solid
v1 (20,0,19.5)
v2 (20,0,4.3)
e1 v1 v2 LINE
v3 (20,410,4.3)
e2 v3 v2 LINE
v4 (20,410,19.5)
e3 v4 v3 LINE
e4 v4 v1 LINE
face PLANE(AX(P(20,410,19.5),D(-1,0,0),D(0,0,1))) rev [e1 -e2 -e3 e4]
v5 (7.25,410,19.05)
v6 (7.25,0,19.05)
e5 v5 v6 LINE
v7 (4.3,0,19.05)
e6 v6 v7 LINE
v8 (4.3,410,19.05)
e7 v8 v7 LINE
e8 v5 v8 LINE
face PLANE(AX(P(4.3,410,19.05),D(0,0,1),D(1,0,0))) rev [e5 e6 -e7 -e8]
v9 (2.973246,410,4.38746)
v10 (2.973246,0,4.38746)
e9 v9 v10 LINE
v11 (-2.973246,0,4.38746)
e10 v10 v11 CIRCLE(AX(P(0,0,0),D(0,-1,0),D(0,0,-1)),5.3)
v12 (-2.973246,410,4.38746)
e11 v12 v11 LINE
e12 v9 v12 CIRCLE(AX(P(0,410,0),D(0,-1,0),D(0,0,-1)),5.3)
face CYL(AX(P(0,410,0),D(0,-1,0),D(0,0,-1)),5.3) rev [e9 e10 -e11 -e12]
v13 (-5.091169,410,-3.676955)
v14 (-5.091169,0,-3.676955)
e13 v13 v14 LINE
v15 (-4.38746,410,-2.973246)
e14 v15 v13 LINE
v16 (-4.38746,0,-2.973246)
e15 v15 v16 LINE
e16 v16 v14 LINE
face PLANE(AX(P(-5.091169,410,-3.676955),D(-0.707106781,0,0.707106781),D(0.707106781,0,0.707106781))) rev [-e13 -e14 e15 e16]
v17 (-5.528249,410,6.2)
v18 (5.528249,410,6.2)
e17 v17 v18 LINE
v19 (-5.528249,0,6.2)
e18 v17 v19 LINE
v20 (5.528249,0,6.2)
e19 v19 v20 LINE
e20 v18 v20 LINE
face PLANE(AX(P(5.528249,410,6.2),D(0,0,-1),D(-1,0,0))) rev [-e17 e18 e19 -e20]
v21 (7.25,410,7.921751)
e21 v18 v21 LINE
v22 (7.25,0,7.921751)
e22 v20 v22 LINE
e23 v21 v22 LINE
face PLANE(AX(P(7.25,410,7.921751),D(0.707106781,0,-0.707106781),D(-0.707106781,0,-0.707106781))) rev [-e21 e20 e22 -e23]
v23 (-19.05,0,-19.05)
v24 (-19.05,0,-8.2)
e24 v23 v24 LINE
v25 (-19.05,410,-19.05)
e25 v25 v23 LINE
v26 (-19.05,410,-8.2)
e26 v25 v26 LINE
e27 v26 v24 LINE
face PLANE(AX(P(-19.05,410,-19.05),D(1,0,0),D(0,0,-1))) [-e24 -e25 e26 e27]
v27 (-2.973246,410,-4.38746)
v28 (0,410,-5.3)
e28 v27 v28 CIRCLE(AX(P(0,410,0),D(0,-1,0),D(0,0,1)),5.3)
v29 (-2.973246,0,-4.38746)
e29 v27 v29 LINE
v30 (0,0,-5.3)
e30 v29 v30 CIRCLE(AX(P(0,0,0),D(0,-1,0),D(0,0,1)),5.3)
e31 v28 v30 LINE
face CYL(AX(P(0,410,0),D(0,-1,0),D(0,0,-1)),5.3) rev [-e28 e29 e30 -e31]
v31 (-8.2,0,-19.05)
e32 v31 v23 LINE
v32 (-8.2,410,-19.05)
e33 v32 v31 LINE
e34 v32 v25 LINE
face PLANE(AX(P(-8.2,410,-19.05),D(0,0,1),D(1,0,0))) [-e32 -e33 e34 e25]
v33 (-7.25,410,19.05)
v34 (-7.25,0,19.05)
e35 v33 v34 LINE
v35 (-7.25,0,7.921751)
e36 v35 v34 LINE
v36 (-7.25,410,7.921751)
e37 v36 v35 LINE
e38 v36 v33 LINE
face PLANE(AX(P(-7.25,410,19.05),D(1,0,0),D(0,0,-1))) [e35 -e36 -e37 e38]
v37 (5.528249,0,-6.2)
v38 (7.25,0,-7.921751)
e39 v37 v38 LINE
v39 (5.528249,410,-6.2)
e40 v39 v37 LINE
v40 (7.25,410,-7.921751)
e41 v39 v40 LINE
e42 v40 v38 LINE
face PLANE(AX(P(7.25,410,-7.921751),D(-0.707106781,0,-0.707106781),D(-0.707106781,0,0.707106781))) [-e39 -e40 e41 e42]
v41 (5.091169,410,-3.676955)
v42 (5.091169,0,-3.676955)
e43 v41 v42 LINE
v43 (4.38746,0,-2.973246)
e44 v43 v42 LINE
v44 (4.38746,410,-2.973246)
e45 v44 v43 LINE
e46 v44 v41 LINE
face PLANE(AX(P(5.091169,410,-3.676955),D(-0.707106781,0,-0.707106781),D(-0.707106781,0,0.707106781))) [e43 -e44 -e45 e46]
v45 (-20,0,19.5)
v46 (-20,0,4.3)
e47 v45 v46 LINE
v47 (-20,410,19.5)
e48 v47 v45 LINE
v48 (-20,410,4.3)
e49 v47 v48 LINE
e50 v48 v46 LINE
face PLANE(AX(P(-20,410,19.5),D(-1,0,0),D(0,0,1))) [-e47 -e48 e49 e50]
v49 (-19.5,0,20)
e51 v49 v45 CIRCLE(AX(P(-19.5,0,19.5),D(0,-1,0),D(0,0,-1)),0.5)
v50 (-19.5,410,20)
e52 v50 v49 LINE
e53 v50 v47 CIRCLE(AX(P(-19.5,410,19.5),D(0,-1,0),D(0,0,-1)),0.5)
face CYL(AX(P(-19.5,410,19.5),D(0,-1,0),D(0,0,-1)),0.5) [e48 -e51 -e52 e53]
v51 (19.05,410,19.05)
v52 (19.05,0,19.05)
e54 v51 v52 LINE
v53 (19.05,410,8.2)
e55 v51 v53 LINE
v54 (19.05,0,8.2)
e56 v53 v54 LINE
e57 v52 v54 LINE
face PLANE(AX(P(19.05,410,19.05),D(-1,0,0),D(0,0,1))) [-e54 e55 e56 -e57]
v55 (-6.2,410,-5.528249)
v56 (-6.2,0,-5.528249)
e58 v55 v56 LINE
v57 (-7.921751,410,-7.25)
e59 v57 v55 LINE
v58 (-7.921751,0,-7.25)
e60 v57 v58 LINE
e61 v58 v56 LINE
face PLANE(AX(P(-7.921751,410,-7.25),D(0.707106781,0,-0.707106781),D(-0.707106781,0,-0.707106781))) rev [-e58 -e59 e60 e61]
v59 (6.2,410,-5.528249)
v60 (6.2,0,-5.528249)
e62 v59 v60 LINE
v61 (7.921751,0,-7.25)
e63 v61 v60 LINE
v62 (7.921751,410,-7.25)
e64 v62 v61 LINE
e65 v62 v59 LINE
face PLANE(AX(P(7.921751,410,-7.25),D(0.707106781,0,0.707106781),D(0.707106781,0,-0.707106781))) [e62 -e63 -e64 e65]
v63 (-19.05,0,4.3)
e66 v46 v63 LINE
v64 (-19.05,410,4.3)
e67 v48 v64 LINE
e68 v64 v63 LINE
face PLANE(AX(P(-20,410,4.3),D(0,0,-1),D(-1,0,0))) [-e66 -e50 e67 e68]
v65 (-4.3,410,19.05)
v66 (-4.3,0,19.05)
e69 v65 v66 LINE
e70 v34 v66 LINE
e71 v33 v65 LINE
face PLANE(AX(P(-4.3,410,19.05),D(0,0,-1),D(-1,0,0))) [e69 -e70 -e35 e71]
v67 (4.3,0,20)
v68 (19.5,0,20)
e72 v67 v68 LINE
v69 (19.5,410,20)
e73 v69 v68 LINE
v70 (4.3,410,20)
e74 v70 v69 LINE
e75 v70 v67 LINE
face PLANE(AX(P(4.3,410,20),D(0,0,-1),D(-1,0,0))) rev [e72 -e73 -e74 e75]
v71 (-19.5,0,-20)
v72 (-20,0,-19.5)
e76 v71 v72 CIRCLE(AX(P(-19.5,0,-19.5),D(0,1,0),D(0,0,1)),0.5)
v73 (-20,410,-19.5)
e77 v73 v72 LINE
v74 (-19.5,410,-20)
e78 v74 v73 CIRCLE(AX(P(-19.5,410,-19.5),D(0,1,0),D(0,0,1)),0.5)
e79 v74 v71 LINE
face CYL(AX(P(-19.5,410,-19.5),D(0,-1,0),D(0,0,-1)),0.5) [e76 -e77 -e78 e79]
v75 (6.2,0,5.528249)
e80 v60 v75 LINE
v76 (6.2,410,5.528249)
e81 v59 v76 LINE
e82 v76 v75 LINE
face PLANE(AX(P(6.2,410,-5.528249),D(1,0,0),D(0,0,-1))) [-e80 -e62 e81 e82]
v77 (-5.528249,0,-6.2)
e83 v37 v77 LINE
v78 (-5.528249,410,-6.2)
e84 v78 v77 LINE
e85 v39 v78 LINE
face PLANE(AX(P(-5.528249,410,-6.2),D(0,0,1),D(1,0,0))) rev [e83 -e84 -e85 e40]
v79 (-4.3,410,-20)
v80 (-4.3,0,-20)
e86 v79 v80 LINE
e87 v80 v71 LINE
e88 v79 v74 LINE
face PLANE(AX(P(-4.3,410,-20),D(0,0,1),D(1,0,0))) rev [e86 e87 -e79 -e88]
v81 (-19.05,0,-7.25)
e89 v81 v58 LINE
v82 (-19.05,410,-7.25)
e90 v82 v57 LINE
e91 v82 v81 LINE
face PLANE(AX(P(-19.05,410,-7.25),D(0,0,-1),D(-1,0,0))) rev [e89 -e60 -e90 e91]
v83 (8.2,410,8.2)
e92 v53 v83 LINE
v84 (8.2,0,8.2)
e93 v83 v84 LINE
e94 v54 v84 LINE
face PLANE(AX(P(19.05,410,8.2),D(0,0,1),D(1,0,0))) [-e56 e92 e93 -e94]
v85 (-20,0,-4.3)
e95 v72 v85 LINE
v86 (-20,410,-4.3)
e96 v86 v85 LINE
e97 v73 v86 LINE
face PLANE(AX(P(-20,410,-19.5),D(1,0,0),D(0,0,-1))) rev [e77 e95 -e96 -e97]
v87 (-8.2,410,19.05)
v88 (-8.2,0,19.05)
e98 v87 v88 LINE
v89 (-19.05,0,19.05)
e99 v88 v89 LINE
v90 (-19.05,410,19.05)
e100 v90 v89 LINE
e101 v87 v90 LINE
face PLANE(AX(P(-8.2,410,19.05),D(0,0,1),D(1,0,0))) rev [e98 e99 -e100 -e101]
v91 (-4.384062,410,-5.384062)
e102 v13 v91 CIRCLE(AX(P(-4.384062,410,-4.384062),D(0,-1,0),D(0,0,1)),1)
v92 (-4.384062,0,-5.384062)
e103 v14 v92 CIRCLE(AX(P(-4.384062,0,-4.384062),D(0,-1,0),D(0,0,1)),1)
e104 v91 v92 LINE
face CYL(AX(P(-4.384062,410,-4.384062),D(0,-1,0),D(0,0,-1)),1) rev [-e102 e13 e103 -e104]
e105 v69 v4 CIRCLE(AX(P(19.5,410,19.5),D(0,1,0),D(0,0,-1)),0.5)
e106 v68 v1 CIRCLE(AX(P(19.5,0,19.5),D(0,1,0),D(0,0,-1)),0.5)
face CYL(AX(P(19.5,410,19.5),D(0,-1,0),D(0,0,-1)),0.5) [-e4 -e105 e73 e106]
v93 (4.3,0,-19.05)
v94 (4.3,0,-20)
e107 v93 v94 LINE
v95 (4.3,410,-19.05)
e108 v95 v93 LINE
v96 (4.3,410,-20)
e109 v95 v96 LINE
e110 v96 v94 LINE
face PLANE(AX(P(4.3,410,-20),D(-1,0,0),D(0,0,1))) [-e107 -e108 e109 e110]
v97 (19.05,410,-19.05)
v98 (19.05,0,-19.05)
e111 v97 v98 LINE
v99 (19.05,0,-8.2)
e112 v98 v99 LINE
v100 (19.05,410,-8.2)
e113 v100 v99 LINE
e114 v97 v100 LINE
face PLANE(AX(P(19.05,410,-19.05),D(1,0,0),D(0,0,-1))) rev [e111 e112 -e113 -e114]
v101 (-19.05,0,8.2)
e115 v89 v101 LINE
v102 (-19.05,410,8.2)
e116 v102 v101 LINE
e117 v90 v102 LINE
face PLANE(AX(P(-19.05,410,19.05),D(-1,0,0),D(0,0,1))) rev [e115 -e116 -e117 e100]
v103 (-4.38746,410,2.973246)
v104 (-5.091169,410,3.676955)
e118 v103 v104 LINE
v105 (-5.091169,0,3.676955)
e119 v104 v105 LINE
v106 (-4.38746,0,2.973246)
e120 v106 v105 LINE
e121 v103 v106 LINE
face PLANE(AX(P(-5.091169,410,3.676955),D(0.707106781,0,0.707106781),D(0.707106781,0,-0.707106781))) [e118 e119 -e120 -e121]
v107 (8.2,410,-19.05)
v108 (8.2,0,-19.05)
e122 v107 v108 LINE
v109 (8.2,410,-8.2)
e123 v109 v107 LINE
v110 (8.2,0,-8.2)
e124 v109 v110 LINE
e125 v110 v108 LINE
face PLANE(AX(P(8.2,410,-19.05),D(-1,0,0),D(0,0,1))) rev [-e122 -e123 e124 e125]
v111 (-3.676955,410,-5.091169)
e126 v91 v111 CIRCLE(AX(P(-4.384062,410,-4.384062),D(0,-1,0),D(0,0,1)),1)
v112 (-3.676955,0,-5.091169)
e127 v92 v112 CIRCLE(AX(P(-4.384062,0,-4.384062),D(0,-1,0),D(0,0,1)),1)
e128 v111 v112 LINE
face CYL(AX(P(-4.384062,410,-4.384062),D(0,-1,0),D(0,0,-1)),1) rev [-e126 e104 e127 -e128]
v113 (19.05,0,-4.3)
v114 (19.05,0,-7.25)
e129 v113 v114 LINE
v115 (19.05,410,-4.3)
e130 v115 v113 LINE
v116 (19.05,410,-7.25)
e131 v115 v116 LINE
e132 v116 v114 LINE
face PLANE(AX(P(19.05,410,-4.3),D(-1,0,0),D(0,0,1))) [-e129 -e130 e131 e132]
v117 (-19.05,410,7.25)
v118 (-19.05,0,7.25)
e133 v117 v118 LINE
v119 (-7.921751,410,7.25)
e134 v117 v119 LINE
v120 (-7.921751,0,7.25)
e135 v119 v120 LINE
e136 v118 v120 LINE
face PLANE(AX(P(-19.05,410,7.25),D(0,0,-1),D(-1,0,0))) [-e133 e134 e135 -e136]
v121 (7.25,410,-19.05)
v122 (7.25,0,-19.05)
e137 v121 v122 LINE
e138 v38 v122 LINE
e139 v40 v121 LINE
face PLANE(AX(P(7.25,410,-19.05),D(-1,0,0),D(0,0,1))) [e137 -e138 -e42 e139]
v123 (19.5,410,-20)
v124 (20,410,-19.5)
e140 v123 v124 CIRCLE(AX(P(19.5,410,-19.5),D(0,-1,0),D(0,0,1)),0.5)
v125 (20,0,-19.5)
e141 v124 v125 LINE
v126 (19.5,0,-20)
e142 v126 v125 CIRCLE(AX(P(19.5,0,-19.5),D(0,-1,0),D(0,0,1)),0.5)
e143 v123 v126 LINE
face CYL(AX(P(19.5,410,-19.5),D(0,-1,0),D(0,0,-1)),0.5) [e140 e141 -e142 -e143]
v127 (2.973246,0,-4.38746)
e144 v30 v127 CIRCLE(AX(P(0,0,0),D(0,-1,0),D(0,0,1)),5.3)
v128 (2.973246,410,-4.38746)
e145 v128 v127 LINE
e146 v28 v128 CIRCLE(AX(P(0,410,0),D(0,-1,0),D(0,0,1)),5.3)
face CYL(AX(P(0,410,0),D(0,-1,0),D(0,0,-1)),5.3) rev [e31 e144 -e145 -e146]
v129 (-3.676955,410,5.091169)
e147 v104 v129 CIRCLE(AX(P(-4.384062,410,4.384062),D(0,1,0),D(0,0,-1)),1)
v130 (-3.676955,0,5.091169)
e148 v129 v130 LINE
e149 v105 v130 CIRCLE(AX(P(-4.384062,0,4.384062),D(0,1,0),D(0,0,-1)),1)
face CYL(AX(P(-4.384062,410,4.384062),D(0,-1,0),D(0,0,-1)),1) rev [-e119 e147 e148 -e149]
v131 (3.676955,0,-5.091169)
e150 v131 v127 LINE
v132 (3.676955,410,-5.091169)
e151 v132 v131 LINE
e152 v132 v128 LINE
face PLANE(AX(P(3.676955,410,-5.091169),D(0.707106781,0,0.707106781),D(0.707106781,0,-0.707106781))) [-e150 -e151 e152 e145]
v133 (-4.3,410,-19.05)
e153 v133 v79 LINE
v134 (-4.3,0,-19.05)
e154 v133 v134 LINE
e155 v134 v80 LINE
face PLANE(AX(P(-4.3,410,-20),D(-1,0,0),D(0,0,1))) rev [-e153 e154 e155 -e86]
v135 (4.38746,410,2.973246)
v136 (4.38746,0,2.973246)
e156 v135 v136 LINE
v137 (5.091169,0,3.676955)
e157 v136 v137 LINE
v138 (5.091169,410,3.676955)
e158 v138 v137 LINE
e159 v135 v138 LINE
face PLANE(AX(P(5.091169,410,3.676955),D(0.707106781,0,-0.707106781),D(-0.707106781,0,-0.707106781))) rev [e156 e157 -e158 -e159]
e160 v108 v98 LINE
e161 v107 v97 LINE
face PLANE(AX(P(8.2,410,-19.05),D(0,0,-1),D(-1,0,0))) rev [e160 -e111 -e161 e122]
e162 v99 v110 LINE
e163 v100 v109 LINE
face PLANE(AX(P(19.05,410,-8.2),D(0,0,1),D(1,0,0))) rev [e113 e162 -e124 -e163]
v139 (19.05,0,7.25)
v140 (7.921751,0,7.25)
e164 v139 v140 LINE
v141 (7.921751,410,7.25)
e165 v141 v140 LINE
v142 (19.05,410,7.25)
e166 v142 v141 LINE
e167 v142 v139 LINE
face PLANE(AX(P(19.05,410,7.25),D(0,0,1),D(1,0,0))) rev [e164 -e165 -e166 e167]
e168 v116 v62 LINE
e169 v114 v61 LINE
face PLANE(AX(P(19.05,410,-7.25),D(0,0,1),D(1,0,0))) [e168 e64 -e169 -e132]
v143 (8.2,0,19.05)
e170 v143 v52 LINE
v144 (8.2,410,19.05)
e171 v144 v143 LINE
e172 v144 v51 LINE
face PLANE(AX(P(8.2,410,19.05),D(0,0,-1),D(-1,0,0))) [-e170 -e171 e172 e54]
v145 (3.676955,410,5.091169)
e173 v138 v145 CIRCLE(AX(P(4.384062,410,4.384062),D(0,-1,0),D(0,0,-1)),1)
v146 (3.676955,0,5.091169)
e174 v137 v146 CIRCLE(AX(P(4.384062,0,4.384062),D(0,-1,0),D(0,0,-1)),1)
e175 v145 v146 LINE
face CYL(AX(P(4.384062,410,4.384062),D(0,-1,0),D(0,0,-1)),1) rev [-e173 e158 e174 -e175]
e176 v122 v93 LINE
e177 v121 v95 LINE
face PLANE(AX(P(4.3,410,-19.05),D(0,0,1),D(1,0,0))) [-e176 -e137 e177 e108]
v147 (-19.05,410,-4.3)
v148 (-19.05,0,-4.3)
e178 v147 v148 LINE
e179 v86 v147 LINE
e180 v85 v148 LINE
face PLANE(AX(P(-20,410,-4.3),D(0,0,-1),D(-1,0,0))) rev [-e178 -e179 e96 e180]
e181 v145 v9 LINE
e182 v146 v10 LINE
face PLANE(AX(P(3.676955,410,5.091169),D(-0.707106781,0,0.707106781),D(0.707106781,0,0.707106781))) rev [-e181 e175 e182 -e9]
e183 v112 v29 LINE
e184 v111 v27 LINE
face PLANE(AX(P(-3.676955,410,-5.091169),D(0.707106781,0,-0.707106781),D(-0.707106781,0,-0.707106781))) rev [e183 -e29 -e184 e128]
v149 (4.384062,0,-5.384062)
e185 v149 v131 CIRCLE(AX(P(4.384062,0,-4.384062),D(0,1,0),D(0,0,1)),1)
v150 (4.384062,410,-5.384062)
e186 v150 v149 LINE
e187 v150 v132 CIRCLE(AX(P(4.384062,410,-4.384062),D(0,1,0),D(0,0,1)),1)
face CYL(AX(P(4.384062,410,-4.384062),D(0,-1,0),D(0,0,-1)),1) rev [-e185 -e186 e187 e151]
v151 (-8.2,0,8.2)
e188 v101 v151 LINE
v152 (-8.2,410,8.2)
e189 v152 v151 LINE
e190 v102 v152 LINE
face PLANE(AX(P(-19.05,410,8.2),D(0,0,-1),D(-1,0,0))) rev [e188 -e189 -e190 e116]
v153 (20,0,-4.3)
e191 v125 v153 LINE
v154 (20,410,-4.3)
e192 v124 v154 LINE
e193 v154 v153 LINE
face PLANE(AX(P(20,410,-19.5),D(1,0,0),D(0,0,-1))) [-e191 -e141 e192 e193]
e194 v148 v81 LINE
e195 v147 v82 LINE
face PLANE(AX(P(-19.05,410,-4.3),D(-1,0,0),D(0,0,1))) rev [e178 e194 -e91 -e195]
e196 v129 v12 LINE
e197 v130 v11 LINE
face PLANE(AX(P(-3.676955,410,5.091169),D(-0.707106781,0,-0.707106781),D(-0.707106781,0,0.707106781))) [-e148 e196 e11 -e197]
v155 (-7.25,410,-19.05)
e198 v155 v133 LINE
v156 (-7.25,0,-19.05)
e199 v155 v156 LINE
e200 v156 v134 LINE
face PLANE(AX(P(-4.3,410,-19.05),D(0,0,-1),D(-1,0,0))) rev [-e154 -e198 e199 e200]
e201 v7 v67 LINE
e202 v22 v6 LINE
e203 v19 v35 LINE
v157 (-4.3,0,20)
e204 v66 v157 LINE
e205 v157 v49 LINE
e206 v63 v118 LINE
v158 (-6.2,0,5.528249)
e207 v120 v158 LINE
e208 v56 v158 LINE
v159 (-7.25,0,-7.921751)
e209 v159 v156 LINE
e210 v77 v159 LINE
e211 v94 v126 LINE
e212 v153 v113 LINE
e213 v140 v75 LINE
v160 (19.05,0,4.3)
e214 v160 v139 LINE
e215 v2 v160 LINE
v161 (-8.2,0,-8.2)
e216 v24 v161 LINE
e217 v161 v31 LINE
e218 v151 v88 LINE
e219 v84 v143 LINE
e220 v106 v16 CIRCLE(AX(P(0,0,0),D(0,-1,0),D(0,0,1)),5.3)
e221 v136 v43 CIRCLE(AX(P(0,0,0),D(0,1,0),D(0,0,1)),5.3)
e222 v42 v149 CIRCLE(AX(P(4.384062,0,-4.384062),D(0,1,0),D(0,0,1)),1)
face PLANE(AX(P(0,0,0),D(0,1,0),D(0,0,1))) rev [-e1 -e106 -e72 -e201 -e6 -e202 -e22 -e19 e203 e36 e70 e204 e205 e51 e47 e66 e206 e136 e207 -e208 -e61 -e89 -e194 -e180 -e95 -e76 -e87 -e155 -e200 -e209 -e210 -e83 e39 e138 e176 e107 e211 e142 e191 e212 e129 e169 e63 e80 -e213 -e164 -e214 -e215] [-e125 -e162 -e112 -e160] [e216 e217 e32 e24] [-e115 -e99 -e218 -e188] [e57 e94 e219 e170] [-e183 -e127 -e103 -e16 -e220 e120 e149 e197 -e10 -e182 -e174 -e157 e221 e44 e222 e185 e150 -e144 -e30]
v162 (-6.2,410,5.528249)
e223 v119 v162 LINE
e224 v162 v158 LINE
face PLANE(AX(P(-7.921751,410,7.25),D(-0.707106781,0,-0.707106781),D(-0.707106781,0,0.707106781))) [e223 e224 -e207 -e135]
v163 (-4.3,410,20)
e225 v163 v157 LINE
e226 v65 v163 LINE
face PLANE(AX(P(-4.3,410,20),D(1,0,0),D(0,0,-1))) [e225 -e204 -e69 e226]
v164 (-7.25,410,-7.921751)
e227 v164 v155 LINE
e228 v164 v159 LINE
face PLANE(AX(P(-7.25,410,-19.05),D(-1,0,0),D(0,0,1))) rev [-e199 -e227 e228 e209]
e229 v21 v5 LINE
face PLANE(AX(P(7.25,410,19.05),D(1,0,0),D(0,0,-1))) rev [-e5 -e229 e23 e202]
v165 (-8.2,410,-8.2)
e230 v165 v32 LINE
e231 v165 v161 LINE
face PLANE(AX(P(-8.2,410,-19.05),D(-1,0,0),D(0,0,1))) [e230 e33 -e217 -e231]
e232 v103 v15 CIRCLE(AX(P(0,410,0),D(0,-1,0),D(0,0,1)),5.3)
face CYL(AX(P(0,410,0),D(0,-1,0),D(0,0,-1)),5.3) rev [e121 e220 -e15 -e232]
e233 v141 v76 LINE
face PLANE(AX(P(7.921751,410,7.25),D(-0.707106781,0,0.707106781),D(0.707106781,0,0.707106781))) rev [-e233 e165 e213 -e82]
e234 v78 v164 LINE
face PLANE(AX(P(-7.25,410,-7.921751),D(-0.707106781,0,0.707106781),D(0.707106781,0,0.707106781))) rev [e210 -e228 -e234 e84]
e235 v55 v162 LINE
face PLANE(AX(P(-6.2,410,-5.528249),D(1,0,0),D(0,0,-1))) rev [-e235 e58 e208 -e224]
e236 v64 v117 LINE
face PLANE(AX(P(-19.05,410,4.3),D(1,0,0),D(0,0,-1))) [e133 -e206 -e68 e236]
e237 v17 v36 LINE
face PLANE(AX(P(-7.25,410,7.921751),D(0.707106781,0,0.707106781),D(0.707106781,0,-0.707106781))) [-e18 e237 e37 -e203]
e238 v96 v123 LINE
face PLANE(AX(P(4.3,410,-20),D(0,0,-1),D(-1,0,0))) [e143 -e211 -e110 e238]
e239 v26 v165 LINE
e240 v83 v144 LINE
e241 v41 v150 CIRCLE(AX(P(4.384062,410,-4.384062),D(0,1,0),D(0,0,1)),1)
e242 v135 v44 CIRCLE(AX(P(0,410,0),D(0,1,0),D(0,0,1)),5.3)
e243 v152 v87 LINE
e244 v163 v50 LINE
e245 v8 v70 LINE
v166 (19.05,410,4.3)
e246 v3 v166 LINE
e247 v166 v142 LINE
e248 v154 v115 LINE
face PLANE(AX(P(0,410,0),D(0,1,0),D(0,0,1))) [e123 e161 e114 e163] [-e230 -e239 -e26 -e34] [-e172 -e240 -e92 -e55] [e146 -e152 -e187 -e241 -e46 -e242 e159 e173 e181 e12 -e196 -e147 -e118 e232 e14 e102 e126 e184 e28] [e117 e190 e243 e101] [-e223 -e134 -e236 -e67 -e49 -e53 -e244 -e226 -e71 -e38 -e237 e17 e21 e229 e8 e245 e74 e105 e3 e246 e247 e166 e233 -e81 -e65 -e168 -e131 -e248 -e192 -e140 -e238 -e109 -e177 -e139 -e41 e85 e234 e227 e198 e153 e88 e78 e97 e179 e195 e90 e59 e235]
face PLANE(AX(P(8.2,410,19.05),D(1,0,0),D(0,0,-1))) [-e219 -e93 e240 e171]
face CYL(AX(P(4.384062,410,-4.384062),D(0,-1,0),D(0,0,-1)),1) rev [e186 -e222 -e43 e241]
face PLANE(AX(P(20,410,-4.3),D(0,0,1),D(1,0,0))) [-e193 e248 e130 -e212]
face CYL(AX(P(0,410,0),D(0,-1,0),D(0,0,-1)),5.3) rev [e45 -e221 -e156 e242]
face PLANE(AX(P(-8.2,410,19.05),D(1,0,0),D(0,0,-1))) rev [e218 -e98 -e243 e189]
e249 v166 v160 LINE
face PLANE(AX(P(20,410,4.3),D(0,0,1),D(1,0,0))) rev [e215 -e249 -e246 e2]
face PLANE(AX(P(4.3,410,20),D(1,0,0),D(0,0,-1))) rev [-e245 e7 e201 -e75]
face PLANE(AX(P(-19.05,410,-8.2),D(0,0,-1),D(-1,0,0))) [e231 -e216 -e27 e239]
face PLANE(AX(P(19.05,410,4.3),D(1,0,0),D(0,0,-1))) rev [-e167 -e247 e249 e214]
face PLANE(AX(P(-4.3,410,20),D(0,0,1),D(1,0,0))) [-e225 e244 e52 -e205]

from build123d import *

# Parameters (mm, degrees)
SKETCH1_W               = 10.85
SKETCH1_H               = 10.85
BOSS_EXTRUDE1_DEPTH     = 410
MIRROR2_COPY_1_SKETCH_W = 10.85
MIRROR2_COPY_1_SKETCH_H = 10.85
MIRROR2_COPY_1_DEPTH    = 410


with BuildPart() as part:
    # Sketch1 → Boss-Extrude1 (new body)
    with BuildSketch(Plane(origin=(0, 0, 0), x_dir=(1, 0, 0), z_dir=(0, 1, 0))):
        with BuildLine():
            Line((-4.3, 20), (-19.5, 20))
            ThreePointArc((-19.5, 20), (-19.853553391, 19.853553391), (-20, 19.5))
            Line((-20, 19.5), (-20, 4.3))
            Line((-20, 4.3), (-19.05, 4.3))
            Line((-19.05, 4.3), (-19.05, 7.25))
            Line((-19.05, 7.25), (-7.921751442, 7.25))
            Line((-7.921751442, 7.25), (-6.2, 5.528248558))
            Line((-6.2, 5.528248558), (-6.2, 0))
            Line((-6.2, 0), (-5.3, 0))
            ThreePointArc((-5.3, 0), (-5.066731596, 1.555066215), (-4.387460025, 2.973246463))
            Line((-4.387460025, 2.973246463), (-5.091168825, 3.676955262))
            ThreePointArc((-5.091168825, 3.676955262), (-5.091168825, 5.091168825), (-3.676955262, 5.091168825))
            Line((-3.676955262, 5.091168825), (-2.973246463, 4.387460025))
            ThreePointArc((-2.973246463, 4.387460025), (-1.555066215, 5.066731596), (0, 5.3))
            Line((0, 5.3), (0, 6.2))
            Line((0, 6.2), (-5.528248558, 6.2))
            Line((-5.528248558, 6.2), (-7.25, 7.921751442))
            Line((-7.25, 7.921751442), (-7.25, 19.05))
            Line((-7.25, 19.05), (-4.3, 19.05))
            Line((-4.3, 19.05), (-4.3, 20))
        make_face()
        with Locations((-13.625, 13.625)):
            Rectangle(SKETCH1_W, SKETCH1_H, mode=Mode.SUBTRACT)
    boss_extrude1 = extrude(amount=BOSS_EXTRUDE1_DEPTH)

    # Mirror1: Boss-Extrude1 across plane
    add(boss_extrude1.mirror(Plane(origin=(0, 0, 0), x_dir=(0, 0, 1), z_dir=(1, 0, 0))))

    # Mirror2: Boss-Extrude1 across plane
    add(boss_extrude1.mirror(Plane.XY))

    # Mirror2 copy 1 sketch → Mirror2 copy 1 (add)
    with BuildSketch(Plane(origin=(0, 0, 0), x_dir=(-1, 0, 0), z_dir=(0, 1, 0))):
        with BuildLine():
            Line((-4.3, 20), (-19.5, 20))
            ThreePointArc((-19.5, 20), (-19.853553391, 19.853553391), (-20, 19.5))
            Line((-20, 19.5), (-20, 4.3))
            Line((-20, 4.3), (-19.05, 4.3))
            Line((-19.05, 4.3), (-19.05, 7.25))
            Line((-19.05, 7.25), (-7.921751442, 7.25))
            Line((-7.921751442, 7.25), (-6.2, 5.528248558))
            Line((-6.2, 5.528248558), (-6.2, 0))
            Line((-6.2, 0), (-5.3, 0))
            ThreePointArc((-5.3, 0), (-5.066731596, 1.555066215), (-4.387460025, 2.973246463))
            Line((-4.387460025, 2.973246463), (-5.091168825, 3.676955262))
            ThreePointArc((-5.091168825, 3.676955262), (-5.091168825, 5.091168825), (-3.676955262, 5.091168825))
            Line((-3.676955262, 5.091168825), (-2.973246463, 4.387460025))
            ThreePointArc((-2.973246463, 4.387460025), (-1.555066215, 5.066731596), (0, 5.3))
            Line((0, 5.3), (0, 6.2))
            Line((0, 6.2), (-5.528248558, 6.2))
            Line((-5.528248558, 6.2), (-7.25, 7.921751442))
            Line((-7.25, 7.921751442), (-7.25, 19.05))
            Line((-7.25, 19.05), (-4.3, 19.05))
            Line((-4.3, 19.05), (-4.3, 20))
        make_face()
        with Locations((-13.625, 13.625)):
            Rectangle(MIRROR2_COPY_1_SKETCH_W, MIRROR2_COPY_1_SKETCH_H, mode=Mode.SUBTRACT)
    extrude(amount=MIRROR2_COPY_1_DEPTH)


solid = part.part
